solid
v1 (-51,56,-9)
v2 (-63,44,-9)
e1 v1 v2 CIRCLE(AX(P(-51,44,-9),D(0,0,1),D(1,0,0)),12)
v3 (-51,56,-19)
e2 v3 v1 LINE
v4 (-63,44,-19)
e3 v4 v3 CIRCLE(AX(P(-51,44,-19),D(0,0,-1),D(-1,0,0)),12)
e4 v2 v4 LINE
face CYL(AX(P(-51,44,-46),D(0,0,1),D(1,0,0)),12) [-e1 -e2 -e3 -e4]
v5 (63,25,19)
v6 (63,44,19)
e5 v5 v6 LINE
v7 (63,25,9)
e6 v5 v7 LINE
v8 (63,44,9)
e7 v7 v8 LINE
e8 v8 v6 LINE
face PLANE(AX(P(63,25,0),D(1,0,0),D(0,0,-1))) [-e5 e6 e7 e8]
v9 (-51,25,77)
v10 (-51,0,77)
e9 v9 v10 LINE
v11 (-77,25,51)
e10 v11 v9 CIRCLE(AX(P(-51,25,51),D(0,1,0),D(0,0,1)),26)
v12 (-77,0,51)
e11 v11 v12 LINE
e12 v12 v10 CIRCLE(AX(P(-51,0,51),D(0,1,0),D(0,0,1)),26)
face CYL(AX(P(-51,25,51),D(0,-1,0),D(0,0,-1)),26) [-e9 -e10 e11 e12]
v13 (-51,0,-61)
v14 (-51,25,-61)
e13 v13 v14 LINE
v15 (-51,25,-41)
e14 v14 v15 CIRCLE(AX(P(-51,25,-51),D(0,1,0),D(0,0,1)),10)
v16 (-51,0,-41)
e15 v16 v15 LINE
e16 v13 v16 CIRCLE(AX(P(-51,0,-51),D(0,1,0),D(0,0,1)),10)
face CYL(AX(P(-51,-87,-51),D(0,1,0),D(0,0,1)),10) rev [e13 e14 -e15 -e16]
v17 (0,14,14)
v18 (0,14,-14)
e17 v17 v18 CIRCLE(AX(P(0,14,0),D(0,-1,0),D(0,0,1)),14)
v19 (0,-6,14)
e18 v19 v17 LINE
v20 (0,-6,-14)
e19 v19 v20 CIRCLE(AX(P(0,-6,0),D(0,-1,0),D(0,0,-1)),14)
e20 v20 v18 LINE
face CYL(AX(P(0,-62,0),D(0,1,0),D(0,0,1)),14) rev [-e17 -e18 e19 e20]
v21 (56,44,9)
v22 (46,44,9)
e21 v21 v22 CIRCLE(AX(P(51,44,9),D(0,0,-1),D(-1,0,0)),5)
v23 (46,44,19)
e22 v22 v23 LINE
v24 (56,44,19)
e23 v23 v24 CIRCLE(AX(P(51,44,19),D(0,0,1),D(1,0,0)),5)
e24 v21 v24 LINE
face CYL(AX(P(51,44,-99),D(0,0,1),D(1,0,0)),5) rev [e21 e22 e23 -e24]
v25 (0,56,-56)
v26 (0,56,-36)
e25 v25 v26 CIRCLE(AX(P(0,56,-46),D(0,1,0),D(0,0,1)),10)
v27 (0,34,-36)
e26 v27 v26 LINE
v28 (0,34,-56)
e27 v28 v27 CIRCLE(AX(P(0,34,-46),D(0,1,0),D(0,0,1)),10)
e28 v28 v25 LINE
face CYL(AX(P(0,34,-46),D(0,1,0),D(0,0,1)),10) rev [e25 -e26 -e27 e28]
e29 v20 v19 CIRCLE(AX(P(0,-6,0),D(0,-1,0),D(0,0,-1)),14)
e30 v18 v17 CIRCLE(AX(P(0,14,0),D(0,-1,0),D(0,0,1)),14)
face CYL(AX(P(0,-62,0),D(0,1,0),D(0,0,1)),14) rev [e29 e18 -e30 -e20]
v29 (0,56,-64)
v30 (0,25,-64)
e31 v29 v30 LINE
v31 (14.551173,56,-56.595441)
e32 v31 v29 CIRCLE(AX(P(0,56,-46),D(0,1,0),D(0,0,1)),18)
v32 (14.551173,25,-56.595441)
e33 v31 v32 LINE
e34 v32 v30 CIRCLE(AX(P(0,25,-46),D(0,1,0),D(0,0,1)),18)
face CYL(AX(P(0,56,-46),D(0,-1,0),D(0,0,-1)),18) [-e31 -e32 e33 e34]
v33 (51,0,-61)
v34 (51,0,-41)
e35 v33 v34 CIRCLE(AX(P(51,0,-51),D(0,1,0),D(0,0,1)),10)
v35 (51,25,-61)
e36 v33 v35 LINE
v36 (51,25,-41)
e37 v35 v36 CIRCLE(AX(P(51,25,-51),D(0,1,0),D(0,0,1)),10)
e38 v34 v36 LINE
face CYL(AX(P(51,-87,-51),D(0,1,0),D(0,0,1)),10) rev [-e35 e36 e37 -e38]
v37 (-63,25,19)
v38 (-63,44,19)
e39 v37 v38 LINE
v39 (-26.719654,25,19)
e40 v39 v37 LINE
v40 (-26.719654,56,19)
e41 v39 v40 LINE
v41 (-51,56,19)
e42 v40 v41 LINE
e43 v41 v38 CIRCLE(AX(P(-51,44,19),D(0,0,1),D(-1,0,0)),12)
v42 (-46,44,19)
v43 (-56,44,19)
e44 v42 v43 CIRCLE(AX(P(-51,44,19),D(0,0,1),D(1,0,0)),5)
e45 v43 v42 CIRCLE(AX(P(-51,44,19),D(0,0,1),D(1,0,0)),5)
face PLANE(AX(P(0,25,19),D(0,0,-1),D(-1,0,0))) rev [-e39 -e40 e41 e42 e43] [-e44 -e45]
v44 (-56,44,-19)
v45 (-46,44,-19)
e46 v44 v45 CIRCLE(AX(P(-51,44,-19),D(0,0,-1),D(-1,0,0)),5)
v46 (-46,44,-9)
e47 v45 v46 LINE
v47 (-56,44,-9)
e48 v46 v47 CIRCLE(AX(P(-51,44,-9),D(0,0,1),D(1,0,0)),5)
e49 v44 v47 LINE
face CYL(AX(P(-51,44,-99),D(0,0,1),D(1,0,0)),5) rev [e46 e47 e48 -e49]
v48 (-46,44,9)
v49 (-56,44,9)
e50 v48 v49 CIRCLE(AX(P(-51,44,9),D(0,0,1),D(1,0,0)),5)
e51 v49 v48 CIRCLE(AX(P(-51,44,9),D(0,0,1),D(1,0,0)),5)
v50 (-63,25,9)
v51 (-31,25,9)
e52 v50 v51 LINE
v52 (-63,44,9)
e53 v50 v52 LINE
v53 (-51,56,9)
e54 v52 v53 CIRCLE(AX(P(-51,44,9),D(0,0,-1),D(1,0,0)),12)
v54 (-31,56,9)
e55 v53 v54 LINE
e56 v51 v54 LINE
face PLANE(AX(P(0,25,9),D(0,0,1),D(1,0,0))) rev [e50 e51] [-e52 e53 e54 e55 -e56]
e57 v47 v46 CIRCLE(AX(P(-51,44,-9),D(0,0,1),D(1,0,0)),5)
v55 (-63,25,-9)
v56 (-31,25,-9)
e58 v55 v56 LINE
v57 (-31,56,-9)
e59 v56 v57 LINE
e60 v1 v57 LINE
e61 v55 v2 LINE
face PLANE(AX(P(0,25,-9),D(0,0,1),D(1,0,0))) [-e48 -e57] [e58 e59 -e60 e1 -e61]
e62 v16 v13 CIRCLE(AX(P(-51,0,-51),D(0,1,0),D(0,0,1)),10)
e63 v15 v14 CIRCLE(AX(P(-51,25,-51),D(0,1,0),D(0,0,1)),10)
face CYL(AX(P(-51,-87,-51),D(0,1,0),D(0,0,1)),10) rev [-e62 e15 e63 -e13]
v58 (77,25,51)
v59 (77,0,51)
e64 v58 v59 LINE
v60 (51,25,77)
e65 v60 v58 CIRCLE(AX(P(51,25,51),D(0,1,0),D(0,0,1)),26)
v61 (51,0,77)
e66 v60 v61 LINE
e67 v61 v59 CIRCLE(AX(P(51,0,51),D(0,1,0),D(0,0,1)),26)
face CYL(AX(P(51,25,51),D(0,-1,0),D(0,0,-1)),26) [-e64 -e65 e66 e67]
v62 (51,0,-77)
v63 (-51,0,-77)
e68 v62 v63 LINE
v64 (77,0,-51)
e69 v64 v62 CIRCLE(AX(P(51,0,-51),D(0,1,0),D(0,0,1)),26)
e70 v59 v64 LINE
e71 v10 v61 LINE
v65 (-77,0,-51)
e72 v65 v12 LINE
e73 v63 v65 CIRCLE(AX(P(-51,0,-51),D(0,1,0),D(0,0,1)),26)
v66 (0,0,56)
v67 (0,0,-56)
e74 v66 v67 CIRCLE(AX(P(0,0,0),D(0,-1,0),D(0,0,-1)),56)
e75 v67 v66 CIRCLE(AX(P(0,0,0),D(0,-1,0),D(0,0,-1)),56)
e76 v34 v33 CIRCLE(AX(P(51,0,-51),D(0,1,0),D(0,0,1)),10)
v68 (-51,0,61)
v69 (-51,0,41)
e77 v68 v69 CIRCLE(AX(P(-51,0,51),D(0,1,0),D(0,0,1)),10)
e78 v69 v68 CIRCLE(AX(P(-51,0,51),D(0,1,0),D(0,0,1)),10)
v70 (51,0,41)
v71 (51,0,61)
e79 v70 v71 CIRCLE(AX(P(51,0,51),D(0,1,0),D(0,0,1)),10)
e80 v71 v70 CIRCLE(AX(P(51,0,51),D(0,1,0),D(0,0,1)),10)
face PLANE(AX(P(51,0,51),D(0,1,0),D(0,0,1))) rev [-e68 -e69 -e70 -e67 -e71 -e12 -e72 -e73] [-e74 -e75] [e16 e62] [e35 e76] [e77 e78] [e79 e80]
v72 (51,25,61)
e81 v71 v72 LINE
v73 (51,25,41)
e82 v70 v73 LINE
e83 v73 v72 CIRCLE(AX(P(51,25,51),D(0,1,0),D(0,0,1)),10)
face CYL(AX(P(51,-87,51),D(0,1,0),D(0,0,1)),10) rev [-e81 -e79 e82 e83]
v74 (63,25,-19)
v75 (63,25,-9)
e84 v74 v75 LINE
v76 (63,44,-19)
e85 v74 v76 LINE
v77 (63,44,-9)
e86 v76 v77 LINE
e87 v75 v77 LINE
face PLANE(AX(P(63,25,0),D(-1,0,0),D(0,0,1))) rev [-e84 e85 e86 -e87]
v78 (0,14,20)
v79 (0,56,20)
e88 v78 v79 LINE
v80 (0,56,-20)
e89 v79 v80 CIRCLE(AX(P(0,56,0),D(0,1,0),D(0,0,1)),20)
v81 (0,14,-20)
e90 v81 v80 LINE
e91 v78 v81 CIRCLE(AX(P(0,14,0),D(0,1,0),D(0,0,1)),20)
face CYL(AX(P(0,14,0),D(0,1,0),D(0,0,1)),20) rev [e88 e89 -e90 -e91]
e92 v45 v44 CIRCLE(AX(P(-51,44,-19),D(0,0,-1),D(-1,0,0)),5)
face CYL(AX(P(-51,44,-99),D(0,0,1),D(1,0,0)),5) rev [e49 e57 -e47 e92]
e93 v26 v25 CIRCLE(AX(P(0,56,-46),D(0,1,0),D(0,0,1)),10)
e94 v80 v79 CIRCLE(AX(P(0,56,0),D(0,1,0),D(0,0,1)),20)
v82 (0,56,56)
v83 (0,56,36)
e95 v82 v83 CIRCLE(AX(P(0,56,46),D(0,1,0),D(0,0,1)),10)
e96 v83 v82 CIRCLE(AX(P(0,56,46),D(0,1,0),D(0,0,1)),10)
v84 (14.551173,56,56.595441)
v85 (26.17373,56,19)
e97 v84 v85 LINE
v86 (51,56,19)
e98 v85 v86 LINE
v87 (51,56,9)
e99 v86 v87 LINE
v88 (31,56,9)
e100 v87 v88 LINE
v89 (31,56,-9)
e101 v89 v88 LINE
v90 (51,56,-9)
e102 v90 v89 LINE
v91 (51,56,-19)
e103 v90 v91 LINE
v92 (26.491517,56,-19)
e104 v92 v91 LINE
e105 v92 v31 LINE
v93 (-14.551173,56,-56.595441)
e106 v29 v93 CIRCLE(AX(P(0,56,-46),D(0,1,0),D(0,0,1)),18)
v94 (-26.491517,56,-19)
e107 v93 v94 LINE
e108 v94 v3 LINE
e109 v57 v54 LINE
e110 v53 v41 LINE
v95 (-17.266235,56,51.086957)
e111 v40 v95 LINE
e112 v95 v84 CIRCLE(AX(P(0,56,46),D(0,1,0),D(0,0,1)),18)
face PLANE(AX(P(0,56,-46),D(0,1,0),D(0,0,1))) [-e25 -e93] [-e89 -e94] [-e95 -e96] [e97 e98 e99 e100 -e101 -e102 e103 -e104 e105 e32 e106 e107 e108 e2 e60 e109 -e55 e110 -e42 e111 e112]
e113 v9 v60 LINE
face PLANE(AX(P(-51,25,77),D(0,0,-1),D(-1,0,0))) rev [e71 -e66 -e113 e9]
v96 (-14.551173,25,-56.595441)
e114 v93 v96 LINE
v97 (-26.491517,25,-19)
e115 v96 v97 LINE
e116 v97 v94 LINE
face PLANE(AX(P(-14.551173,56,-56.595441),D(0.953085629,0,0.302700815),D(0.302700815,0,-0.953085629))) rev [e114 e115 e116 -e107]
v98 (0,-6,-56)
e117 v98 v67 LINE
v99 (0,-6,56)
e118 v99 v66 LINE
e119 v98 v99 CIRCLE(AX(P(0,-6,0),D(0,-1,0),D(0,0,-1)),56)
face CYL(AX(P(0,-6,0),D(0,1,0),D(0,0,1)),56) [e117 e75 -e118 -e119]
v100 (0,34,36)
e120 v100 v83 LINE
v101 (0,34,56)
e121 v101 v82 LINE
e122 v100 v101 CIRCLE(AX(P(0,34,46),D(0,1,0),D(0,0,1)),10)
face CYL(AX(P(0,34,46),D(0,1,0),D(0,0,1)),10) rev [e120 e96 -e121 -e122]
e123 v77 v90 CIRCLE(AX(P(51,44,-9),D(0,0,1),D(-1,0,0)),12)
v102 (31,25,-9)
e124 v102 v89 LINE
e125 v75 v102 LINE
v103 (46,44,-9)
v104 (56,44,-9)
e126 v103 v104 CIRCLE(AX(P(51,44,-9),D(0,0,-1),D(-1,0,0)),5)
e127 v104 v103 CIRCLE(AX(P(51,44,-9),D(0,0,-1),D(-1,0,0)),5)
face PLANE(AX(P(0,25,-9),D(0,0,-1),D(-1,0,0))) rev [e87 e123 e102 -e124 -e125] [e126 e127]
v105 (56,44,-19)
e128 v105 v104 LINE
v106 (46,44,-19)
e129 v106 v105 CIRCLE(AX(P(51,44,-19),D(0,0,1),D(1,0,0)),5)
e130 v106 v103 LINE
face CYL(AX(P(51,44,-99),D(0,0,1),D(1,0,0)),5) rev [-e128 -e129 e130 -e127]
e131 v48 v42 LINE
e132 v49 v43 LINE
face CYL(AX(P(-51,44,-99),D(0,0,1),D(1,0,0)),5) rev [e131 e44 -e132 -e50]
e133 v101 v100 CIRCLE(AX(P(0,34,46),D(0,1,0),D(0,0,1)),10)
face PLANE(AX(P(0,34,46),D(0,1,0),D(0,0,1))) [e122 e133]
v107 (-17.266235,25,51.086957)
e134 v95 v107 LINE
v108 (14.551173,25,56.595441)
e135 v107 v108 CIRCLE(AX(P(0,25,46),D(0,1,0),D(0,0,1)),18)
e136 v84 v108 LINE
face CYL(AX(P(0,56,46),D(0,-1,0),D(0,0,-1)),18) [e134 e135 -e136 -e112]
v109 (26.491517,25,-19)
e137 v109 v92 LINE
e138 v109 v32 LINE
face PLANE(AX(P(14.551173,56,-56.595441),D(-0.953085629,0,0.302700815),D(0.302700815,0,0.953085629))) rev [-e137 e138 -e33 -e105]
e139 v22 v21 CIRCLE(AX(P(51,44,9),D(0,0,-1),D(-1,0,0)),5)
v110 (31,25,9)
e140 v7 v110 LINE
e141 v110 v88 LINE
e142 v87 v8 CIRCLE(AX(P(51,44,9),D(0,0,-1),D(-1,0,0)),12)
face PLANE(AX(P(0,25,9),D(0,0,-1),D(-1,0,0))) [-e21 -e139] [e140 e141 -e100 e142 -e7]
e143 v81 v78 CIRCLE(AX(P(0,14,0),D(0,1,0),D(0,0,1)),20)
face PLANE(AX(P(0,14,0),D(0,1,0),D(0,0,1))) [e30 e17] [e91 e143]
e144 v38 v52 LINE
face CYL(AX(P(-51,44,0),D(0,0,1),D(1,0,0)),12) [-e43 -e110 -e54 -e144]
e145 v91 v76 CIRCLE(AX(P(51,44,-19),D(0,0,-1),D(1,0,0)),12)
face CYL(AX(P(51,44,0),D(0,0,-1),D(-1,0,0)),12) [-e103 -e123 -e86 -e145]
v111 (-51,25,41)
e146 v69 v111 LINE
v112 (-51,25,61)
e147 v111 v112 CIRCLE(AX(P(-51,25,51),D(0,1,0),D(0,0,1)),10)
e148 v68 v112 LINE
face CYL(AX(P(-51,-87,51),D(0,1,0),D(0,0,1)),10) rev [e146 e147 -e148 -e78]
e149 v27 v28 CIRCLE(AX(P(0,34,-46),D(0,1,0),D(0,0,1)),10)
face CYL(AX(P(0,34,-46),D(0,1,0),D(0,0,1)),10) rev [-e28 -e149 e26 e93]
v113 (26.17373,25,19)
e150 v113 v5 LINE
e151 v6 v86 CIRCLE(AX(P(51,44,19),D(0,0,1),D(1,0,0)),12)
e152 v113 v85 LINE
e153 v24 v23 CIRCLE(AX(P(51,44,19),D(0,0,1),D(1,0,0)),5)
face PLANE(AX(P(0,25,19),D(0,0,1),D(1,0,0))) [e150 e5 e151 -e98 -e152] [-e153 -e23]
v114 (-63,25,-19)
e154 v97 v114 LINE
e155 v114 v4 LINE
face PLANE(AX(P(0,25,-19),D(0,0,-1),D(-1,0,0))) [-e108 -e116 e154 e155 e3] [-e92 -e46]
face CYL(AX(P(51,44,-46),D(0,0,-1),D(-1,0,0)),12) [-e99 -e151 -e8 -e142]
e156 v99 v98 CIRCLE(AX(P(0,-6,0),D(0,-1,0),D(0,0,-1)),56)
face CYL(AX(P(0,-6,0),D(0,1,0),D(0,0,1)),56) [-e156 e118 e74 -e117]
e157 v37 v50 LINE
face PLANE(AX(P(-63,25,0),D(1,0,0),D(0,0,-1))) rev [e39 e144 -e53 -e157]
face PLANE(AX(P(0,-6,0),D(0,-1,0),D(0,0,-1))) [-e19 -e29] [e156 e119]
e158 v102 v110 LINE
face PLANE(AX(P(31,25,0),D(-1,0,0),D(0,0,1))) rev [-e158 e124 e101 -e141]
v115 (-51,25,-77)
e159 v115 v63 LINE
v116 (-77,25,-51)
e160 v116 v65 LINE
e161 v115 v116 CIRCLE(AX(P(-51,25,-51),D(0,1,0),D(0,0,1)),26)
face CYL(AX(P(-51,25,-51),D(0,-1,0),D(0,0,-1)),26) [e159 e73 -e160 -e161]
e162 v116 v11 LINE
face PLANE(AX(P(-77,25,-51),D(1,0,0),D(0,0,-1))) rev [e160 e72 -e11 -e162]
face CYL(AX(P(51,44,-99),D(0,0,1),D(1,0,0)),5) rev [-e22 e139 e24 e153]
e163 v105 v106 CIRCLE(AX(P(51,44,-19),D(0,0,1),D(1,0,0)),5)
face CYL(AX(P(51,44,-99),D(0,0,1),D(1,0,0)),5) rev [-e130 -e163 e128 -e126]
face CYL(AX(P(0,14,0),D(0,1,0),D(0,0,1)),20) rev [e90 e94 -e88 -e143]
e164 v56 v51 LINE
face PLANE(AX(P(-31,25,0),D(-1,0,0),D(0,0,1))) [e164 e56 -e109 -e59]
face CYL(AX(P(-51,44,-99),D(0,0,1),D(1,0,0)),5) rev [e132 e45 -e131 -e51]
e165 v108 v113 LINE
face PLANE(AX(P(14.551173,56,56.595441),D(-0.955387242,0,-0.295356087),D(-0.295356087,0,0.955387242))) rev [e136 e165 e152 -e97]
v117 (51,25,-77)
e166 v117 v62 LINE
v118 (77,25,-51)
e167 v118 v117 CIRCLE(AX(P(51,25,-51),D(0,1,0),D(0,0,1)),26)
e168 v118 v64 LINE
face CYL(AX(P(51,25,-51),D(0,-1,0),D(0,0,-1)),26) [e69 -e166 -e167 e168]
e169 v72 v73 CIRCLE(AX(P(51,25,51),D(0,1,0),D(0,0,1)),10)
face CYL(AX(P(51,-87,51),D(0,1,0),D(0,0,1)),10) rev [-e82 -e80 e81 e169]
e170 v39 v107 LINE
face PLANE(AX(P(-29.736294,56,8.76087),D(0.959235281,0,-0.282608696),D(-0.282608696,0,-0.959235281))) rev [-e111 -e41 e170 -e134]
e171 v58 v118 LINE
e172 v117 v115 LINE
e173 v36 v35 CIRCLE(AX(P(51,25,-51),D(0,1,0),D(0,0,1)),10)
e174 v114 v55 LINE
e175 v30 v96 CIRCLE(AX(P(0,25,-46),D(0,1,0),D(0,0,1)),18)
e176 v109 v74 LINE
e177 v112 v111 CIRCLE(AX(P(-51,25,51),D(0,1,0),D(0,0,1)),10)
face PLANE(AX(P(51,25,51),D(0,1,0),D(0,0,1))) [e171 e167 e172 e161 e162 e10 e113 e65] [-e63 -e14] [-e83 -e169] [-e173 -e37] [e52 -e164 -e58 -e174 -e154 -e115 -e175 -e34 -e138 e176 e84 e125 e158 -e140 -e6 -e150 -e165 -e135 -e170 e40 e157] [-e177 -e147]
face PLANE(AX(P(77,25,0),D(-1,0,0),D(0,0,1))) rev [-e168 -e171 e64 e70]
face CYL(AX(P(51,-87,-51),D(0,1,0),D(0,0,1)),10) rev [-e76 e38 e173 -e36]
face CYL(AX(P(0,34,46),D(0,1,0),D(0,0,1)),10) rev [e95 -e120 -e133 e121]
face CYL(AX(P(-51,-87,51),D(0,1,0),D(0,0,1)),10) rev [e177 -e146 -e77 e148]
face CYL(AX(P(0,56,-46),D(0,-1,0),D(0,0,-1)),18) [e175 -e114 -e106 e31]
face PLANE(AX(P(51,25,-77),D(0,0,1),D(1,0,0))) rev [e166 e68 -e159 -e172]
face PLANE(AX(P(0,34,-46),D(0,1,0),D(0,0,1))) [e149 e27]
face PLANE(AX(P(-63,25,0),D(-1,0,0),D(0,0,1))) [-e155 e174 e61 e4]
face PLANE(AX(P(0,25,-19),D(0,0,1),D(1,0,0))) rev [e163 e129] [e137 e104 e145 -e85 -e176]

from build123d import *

# Parameters (mm, degrees)
BASE_PLATE_DEPTH              = 25
PLATE_MOUNTING_HOLES_SKETCH_R = 10
PLATE_MOUNTING_HOLES_DEPTH    = 112
CENTRAL_BOSS_DEPTH            = 31
LUG_START                     = -31
LUG_PAIR_A_DEPTH              = 31
LUG_PAIR_B_DEPTH              = 31
LUG_PIN_HOLES_SKETCH_R        = 5
LUG_PIN_HOLES_DEPTH           = 118
LUG_A_FILLET_1_R              = 12
LUG_A_FILLET_2_R              = 12
LUG_B_FILLET_1_R              = 12
LUG_B_FILLET_2_R              = 12
CENTRAL_BORE_SKETCH_R         = 14
CENTRAL_BORE_DEPTH            = 118
BORE_COUNTERBORE_SKETCH_R     = 20
BORE_COUNTERBORE_DEPTH        = 42
BOTTOM_SPIGOT_SKETCH_R        = 56
BOTTOM_SPIGOT_DEPTH           = 6
SPIGOT_BORE_SKETCH_R          = 14
SPIGOT_BORE_DEPTH             = 120
FLANGE_HOLE_1_SKETCH_R        = 10
FLANGE_HOLE_1_DEPTH           = 22
FLANGE_HOLE_2_SKETCH_R        = 10
FLANGE_HOLE_2_DEPTH           = 22


with BuildPart() as part:
    # Base Plate Sketch → Base Plate (new body)
    with BuildSketch(Plane(origin=(0, 0, 0), x_dir=(1, 0, 0), z_dir=(0, 1, 0))):
        with BuildLine():
            Line((77, 0), (77, 51))
            ThreePointArc((77, 51), (69.384776311, 69.384776311), (51, 77))
            Line((51, 77), (-51, 77))
            ThreePointArc((-51, 77), (-69.384776311, 69.384776311), (-77, 51))
            Line((-77, 51), (-77, -51))
            ThreePointArc((-77, -51), (-69.384776311, -69.384776311), (-51, -77))
            Line((-51, -77), (51, -77))
            ThreePointArc((51, -77), (69.384776311, -69.384776311), (77, -51))
            Line((77, -51), (77, 0))
        make_face()
    extrude(amount=BASE_PLATE_DEPTH)

    # Plate Mounting Holes Sketch → Plate Mounting Holes (cut)
    with BuildSketch(Plane(origin=(0, 25, 0), x_dir=(1, 0, 0), z_dir=(0, 1, 0))):
        with Locations(Location((-51, 51, 0), (0, 0, 270))):
            Circle(PLATE_MOUNTING_HOLES_SKETCH_R)
        with Locations(Location((51, 51, 0), (0, 0, 270))):
            Circle(PLATE_MOUNTING_HOLES_SKETCH_R)
        with Locations(Location((51, -51, 0), (0, 0, 270))):
            Circle(PLATE_MOUNTING_HOLES_SKETCH_R)
        with Locations(Location((-51, -51, 0), (0, 0, 270))):
            Circle(PLATE_MOUNTING_HOLES_SKETCH_R)
    extrude(amount=-PLATE_MOUNTING_HOLES_DEPTH, mode=Mode.SUBTRACT)

    # Central Boss Sketch → Central Boss (add)
    with BuildSketch(Plane(origin=(0, 25, 0), x_dir=(1, 0, 0), z_dir=(0, 1, 0))):
        with BuildLine():
            Line((14.551173168, 56.595440502), (29.545654505, 9.383725265))
            ThreePointArc((29.545654505, 9.383725265), (30.89470992, 2.552821763), (30.685167625, -4.406868258))
            Line((30.685167625, -4.406868258), (14.551173168, -56.595440502))
            ThreePointArc((14.551173168, -56.595440502), (-3.070625216, -63.736156878), (-17.266235066, -51.086956522))
            Line((-17.266235066, -51.086956522), (-29.736293724, -8.760869565))
            ThreePointArc((-29.736293724, -8.760869565), (-30.998289096, 0.325688707), (-29.545654505, 9.383725265))
            Line((-29.545654505, 9.383725265), (-14.551173168, 56.595440502))
            ThreePointArc((-14.551173168, 56.595440502), (0, 64), (14.551173168, 56.595440502))
        make_face()
    extrude(amount=CENTRAL_BOSS_DEPTH)

    # Lug Pair A Sketch → Lug Pair A (add)
    with BuildSketch(Plane(origin=(0, 56, 0), x_dir=(1, 0, 0), z_dir=(0, 1, 0)).offset(LUG_START)):
        with BuildLine():
            Line((31, 0), (31, 9))
            Line((31, 9), (63, 9))
            Line((63, 9), (63, 19))
            Line((63, 19), (31, 19))
            Line((31, 19), (26.491517384, 19))
            Line((26.491517384, 19), (29.545654505, 9.383725265))
            ThreePointArc((29.545654505, 9.383725265), (30.634256068, 4.747879018), (31, 0))
        make_face()
        with BuildLine():
            Line((31, -9), (31, 0))
            ThreePointArc((31, 0), (30.921191733, -2.209049981), (30.685167625, -4.406868258))
            ThreePointArc((30.685167625, -4.406868258), (29.6170045, -9.156038686), (27.818568264, -13.679446617))
            Line((27.818568264, -13.679446617), (26.173729651, -19))
            Line((26.173729651, -19), (31, -19))
            Line((31, -19), (63, -19))
            Line((63, -19), (63, -9))
            Line((63, -9), (31, -9))
        make_face()
        with BuildLine():
            ThreePointArc((24.494897428, 19), (27.444735347, 14.414801481), (29.545654505, 9.383725265))
            Line((29.545654505, 9.383725265), (26.491517384, 19))
            Line((26.491517384, 19), (24.494897428, 19))
        make_face()
        with BuildLine():
            Line((26.173729651, -19), (27.818568264, -13.679446617))
            ThreePointArc((27.818568264, -13.679446617), (26.29166684, -16.424014575), (24.494897428, -19))
            Line((24.494897428, -19), (26.173729651, -19))
        make_face()
        with BuildLine():
            ThreePointArc((27.818568264, -13.679446617), (29.6170045, -9.156038686), (30.685167625, -4.406868258))
            Line((30.685167625, -4.406868258), (27.818568264, -13.679446617))
        make_face()
    extrude(amount=LUG_PAIR_A_DEPTH)

    # Lug Pair B Sketch → Lug Pair B (add)
    with BuildSketch(Plane(origin=(0, 56, 0), x_dir=(1, 0, 0), z_dir=(0, 1, 0)).offset(LUG_START)):
        with BuildLine():
            ThreePointArc((-29.736293724, -8.760869565), (-30.682446981, -4.425770811), (-31, 0))
            Line((-31, 0), (-31, -9))
            Line((-31, -9), (-63, -9))
            Line((-63, -9), (-63, -19))
            Line((-63, -19), (-26.719653956, -19))
            Line((-26.719653956, -19), (-29.736293724, -8.760869565))
        make_face()
        with BuildLine():
            Line((-31, 9), (-31, 0))
            ThreePointArc((-31, 0), (-30.634256068, 4.747879018), (-29.545654505, 9.383725265))
            Line((-29.545654505, 9.383725265), (-26.491517384, 19))
            Line((-26.491517384, 19), (-63, 19))
            Line((-63, 19), (-63, 9))
            Line((-63, 9), (-31, 9))
        make_face()
        with BuildLine():
            ThreePointArc((-24.494897428, -19), (-27.594663822, -14.125669136), (-29.736293724, -8.760869565))
            Line((-29.736293724, -8.760869565), (-26.719653956, -19))
            Line((-26.719653956, -19), (-24.494897428, -19))
        make_face()
        with BuildLine():
            Line((-26.491517384, 19), (-29.545654505, 9.383725265))
            ThreePointArc((-29.545654505, 9.383725265), (-27.444735347, 14.414801481), (-24.494897428, 19))
            Line((-24.494897428, 19), (-26.491517384, 19))
        make_face()
    extrude(amount=LUG_PAIR_B_DEPTH)

    # Lug Pin Holes Sketch → Lug Pin Holes (cut)
    with BuildSketch(Plane.XY.offset(19)):
        with Locations((51, 44)):
            Circle(LUG_PIN_HOLES_SKETCH_R)
        with Locations((-51, 44)):
            Circle(LUG_PIN_HOLES_SKETCH_R)
    extrude(amount=-LUG_PIN_HOLES_DEPTH, mode=Mode.SUBTRACT)

    # Lug A Fillet 1
    lug_a_fillet_1_edges = [part.edges().sort_by_distance(p)[0] for p in [
        (63, 56, 14),
    ]]
    fillet(lug_a_fillet_1_edges, radius=LUG_A_FILLET_1_R)

    # Lug A Fillet 2
    lug_a_fillet_2_edges = [part.edges().sort_by_distance(p)[0] for p in [
        (63, 56, -14),
    ]]
    fillet(lug_a_fillet_2_edges, radius=LUG_A_FILLET_2_R)

    # Lug B Fillet 1
    lug_b_fillet_1_edges = [part.edges().sort_by_distance(p)[0] for p in [
        (-63, 56, -14),
    ]]
    fillet(lug_b_fillet_1_edges, radius=LUG_B_FILLET_1_R)

    # Lug B Fillet 2
    lug_b_fillet_2_edges = [part.edges().sort_by_distance(p)[0] for p in [
        (-63, 56, 14),
    ]]
    fillet(lug_b_fillet_2_edges, radius=LUG_B_FILLET_2_R)

    # Central Bore Sketch → Central Bore (cut)
    with BuildSketch(Plane(origin=(0, 56, 0), x_dir=(1, 0, 0), z_dir=(0, 1, 0))):
        with Locations(Location((0, 0, 0), (0, 0, 270))):
            Circle(CENTRAL_BORE_SKETCH_R)
    extrude(amount=-CENTRAL_BORE_DEPTH, mode=Mode.SUBTRACT)

    # Bore Counterbore Sketch → Bore Counterbore (cut)
    with BuildSketch(Plane(origin=(0, 56, 0), x_dir=(1, 0, 0), z_dir=(0, 1, 0))):
        with Locations(Location((0, 0, 0), (0, 0, 270))):
            Circle(BORE_COUNTERBORE_SKETCH_R)
    extrude(amount=-BORE_COUNTERBORE_DEPTH, mode=Mode.SUBTRACT)

    # Bottom Spigot Sketch → Bottom Spigot (add)
    with BuildSketch(Plane.XZ):
        with Locations(Location((0, 0, 0), (0, 0, 270))):
            Circle(BOTTOM_SPIGOT_SKETCH_R)
    extrude(amount=BOTTOM_SPIGOT_DEPTH)

    # Spigot Bore Sketch → Spigot Bore (cut)
    with BuildSketch(Plane(origin=(0, 0, 0), x_dir=(1, 0, 0), z_dir=(0, 1, 0))):
        with Locations(Location((0, 0, 0), (0, 0, 270))):
            Circle(SPIGOT_BORE_SKETCH_R)
    extrude(amount=-SPIGOT_BORE_DEPTH, mode=Mode.SUBTRACT)

    # Flange Hole 1 Sketch → Flange Hole 1 (cut)
    with BuildSketch(Plane(origin=(0, 56, 0), x_dir=(1, 0, 0), z_dir=(0, 1, 0))):
        with Locations(Location((0, 46, 0), (0, 0, 270))):
            Circle(FLANGE_HOLE_1_SKETCH_R)
    extrude(amount=-FLANGE_HOLE_1_DEPTH, mode=Mode.SUBTRACT)

    # Flange Hole 2 Sketch → Flange Hole 2 (cut)
    with BuildSketch(Plane(origin=(0, 56, 0), x_dir=(1, 0, 0), z_dir=(0, 1, 0))):
        with Locations(Location((0, -46, 0), (0, 0, 270))):
            Circle(FLANGE_HOLE_2_SKETCH_R)
    extrude(amount=-FLANGE_HOLE_2_DEPTH, mode=Mode.SUBTRACT)


solid = part.part
